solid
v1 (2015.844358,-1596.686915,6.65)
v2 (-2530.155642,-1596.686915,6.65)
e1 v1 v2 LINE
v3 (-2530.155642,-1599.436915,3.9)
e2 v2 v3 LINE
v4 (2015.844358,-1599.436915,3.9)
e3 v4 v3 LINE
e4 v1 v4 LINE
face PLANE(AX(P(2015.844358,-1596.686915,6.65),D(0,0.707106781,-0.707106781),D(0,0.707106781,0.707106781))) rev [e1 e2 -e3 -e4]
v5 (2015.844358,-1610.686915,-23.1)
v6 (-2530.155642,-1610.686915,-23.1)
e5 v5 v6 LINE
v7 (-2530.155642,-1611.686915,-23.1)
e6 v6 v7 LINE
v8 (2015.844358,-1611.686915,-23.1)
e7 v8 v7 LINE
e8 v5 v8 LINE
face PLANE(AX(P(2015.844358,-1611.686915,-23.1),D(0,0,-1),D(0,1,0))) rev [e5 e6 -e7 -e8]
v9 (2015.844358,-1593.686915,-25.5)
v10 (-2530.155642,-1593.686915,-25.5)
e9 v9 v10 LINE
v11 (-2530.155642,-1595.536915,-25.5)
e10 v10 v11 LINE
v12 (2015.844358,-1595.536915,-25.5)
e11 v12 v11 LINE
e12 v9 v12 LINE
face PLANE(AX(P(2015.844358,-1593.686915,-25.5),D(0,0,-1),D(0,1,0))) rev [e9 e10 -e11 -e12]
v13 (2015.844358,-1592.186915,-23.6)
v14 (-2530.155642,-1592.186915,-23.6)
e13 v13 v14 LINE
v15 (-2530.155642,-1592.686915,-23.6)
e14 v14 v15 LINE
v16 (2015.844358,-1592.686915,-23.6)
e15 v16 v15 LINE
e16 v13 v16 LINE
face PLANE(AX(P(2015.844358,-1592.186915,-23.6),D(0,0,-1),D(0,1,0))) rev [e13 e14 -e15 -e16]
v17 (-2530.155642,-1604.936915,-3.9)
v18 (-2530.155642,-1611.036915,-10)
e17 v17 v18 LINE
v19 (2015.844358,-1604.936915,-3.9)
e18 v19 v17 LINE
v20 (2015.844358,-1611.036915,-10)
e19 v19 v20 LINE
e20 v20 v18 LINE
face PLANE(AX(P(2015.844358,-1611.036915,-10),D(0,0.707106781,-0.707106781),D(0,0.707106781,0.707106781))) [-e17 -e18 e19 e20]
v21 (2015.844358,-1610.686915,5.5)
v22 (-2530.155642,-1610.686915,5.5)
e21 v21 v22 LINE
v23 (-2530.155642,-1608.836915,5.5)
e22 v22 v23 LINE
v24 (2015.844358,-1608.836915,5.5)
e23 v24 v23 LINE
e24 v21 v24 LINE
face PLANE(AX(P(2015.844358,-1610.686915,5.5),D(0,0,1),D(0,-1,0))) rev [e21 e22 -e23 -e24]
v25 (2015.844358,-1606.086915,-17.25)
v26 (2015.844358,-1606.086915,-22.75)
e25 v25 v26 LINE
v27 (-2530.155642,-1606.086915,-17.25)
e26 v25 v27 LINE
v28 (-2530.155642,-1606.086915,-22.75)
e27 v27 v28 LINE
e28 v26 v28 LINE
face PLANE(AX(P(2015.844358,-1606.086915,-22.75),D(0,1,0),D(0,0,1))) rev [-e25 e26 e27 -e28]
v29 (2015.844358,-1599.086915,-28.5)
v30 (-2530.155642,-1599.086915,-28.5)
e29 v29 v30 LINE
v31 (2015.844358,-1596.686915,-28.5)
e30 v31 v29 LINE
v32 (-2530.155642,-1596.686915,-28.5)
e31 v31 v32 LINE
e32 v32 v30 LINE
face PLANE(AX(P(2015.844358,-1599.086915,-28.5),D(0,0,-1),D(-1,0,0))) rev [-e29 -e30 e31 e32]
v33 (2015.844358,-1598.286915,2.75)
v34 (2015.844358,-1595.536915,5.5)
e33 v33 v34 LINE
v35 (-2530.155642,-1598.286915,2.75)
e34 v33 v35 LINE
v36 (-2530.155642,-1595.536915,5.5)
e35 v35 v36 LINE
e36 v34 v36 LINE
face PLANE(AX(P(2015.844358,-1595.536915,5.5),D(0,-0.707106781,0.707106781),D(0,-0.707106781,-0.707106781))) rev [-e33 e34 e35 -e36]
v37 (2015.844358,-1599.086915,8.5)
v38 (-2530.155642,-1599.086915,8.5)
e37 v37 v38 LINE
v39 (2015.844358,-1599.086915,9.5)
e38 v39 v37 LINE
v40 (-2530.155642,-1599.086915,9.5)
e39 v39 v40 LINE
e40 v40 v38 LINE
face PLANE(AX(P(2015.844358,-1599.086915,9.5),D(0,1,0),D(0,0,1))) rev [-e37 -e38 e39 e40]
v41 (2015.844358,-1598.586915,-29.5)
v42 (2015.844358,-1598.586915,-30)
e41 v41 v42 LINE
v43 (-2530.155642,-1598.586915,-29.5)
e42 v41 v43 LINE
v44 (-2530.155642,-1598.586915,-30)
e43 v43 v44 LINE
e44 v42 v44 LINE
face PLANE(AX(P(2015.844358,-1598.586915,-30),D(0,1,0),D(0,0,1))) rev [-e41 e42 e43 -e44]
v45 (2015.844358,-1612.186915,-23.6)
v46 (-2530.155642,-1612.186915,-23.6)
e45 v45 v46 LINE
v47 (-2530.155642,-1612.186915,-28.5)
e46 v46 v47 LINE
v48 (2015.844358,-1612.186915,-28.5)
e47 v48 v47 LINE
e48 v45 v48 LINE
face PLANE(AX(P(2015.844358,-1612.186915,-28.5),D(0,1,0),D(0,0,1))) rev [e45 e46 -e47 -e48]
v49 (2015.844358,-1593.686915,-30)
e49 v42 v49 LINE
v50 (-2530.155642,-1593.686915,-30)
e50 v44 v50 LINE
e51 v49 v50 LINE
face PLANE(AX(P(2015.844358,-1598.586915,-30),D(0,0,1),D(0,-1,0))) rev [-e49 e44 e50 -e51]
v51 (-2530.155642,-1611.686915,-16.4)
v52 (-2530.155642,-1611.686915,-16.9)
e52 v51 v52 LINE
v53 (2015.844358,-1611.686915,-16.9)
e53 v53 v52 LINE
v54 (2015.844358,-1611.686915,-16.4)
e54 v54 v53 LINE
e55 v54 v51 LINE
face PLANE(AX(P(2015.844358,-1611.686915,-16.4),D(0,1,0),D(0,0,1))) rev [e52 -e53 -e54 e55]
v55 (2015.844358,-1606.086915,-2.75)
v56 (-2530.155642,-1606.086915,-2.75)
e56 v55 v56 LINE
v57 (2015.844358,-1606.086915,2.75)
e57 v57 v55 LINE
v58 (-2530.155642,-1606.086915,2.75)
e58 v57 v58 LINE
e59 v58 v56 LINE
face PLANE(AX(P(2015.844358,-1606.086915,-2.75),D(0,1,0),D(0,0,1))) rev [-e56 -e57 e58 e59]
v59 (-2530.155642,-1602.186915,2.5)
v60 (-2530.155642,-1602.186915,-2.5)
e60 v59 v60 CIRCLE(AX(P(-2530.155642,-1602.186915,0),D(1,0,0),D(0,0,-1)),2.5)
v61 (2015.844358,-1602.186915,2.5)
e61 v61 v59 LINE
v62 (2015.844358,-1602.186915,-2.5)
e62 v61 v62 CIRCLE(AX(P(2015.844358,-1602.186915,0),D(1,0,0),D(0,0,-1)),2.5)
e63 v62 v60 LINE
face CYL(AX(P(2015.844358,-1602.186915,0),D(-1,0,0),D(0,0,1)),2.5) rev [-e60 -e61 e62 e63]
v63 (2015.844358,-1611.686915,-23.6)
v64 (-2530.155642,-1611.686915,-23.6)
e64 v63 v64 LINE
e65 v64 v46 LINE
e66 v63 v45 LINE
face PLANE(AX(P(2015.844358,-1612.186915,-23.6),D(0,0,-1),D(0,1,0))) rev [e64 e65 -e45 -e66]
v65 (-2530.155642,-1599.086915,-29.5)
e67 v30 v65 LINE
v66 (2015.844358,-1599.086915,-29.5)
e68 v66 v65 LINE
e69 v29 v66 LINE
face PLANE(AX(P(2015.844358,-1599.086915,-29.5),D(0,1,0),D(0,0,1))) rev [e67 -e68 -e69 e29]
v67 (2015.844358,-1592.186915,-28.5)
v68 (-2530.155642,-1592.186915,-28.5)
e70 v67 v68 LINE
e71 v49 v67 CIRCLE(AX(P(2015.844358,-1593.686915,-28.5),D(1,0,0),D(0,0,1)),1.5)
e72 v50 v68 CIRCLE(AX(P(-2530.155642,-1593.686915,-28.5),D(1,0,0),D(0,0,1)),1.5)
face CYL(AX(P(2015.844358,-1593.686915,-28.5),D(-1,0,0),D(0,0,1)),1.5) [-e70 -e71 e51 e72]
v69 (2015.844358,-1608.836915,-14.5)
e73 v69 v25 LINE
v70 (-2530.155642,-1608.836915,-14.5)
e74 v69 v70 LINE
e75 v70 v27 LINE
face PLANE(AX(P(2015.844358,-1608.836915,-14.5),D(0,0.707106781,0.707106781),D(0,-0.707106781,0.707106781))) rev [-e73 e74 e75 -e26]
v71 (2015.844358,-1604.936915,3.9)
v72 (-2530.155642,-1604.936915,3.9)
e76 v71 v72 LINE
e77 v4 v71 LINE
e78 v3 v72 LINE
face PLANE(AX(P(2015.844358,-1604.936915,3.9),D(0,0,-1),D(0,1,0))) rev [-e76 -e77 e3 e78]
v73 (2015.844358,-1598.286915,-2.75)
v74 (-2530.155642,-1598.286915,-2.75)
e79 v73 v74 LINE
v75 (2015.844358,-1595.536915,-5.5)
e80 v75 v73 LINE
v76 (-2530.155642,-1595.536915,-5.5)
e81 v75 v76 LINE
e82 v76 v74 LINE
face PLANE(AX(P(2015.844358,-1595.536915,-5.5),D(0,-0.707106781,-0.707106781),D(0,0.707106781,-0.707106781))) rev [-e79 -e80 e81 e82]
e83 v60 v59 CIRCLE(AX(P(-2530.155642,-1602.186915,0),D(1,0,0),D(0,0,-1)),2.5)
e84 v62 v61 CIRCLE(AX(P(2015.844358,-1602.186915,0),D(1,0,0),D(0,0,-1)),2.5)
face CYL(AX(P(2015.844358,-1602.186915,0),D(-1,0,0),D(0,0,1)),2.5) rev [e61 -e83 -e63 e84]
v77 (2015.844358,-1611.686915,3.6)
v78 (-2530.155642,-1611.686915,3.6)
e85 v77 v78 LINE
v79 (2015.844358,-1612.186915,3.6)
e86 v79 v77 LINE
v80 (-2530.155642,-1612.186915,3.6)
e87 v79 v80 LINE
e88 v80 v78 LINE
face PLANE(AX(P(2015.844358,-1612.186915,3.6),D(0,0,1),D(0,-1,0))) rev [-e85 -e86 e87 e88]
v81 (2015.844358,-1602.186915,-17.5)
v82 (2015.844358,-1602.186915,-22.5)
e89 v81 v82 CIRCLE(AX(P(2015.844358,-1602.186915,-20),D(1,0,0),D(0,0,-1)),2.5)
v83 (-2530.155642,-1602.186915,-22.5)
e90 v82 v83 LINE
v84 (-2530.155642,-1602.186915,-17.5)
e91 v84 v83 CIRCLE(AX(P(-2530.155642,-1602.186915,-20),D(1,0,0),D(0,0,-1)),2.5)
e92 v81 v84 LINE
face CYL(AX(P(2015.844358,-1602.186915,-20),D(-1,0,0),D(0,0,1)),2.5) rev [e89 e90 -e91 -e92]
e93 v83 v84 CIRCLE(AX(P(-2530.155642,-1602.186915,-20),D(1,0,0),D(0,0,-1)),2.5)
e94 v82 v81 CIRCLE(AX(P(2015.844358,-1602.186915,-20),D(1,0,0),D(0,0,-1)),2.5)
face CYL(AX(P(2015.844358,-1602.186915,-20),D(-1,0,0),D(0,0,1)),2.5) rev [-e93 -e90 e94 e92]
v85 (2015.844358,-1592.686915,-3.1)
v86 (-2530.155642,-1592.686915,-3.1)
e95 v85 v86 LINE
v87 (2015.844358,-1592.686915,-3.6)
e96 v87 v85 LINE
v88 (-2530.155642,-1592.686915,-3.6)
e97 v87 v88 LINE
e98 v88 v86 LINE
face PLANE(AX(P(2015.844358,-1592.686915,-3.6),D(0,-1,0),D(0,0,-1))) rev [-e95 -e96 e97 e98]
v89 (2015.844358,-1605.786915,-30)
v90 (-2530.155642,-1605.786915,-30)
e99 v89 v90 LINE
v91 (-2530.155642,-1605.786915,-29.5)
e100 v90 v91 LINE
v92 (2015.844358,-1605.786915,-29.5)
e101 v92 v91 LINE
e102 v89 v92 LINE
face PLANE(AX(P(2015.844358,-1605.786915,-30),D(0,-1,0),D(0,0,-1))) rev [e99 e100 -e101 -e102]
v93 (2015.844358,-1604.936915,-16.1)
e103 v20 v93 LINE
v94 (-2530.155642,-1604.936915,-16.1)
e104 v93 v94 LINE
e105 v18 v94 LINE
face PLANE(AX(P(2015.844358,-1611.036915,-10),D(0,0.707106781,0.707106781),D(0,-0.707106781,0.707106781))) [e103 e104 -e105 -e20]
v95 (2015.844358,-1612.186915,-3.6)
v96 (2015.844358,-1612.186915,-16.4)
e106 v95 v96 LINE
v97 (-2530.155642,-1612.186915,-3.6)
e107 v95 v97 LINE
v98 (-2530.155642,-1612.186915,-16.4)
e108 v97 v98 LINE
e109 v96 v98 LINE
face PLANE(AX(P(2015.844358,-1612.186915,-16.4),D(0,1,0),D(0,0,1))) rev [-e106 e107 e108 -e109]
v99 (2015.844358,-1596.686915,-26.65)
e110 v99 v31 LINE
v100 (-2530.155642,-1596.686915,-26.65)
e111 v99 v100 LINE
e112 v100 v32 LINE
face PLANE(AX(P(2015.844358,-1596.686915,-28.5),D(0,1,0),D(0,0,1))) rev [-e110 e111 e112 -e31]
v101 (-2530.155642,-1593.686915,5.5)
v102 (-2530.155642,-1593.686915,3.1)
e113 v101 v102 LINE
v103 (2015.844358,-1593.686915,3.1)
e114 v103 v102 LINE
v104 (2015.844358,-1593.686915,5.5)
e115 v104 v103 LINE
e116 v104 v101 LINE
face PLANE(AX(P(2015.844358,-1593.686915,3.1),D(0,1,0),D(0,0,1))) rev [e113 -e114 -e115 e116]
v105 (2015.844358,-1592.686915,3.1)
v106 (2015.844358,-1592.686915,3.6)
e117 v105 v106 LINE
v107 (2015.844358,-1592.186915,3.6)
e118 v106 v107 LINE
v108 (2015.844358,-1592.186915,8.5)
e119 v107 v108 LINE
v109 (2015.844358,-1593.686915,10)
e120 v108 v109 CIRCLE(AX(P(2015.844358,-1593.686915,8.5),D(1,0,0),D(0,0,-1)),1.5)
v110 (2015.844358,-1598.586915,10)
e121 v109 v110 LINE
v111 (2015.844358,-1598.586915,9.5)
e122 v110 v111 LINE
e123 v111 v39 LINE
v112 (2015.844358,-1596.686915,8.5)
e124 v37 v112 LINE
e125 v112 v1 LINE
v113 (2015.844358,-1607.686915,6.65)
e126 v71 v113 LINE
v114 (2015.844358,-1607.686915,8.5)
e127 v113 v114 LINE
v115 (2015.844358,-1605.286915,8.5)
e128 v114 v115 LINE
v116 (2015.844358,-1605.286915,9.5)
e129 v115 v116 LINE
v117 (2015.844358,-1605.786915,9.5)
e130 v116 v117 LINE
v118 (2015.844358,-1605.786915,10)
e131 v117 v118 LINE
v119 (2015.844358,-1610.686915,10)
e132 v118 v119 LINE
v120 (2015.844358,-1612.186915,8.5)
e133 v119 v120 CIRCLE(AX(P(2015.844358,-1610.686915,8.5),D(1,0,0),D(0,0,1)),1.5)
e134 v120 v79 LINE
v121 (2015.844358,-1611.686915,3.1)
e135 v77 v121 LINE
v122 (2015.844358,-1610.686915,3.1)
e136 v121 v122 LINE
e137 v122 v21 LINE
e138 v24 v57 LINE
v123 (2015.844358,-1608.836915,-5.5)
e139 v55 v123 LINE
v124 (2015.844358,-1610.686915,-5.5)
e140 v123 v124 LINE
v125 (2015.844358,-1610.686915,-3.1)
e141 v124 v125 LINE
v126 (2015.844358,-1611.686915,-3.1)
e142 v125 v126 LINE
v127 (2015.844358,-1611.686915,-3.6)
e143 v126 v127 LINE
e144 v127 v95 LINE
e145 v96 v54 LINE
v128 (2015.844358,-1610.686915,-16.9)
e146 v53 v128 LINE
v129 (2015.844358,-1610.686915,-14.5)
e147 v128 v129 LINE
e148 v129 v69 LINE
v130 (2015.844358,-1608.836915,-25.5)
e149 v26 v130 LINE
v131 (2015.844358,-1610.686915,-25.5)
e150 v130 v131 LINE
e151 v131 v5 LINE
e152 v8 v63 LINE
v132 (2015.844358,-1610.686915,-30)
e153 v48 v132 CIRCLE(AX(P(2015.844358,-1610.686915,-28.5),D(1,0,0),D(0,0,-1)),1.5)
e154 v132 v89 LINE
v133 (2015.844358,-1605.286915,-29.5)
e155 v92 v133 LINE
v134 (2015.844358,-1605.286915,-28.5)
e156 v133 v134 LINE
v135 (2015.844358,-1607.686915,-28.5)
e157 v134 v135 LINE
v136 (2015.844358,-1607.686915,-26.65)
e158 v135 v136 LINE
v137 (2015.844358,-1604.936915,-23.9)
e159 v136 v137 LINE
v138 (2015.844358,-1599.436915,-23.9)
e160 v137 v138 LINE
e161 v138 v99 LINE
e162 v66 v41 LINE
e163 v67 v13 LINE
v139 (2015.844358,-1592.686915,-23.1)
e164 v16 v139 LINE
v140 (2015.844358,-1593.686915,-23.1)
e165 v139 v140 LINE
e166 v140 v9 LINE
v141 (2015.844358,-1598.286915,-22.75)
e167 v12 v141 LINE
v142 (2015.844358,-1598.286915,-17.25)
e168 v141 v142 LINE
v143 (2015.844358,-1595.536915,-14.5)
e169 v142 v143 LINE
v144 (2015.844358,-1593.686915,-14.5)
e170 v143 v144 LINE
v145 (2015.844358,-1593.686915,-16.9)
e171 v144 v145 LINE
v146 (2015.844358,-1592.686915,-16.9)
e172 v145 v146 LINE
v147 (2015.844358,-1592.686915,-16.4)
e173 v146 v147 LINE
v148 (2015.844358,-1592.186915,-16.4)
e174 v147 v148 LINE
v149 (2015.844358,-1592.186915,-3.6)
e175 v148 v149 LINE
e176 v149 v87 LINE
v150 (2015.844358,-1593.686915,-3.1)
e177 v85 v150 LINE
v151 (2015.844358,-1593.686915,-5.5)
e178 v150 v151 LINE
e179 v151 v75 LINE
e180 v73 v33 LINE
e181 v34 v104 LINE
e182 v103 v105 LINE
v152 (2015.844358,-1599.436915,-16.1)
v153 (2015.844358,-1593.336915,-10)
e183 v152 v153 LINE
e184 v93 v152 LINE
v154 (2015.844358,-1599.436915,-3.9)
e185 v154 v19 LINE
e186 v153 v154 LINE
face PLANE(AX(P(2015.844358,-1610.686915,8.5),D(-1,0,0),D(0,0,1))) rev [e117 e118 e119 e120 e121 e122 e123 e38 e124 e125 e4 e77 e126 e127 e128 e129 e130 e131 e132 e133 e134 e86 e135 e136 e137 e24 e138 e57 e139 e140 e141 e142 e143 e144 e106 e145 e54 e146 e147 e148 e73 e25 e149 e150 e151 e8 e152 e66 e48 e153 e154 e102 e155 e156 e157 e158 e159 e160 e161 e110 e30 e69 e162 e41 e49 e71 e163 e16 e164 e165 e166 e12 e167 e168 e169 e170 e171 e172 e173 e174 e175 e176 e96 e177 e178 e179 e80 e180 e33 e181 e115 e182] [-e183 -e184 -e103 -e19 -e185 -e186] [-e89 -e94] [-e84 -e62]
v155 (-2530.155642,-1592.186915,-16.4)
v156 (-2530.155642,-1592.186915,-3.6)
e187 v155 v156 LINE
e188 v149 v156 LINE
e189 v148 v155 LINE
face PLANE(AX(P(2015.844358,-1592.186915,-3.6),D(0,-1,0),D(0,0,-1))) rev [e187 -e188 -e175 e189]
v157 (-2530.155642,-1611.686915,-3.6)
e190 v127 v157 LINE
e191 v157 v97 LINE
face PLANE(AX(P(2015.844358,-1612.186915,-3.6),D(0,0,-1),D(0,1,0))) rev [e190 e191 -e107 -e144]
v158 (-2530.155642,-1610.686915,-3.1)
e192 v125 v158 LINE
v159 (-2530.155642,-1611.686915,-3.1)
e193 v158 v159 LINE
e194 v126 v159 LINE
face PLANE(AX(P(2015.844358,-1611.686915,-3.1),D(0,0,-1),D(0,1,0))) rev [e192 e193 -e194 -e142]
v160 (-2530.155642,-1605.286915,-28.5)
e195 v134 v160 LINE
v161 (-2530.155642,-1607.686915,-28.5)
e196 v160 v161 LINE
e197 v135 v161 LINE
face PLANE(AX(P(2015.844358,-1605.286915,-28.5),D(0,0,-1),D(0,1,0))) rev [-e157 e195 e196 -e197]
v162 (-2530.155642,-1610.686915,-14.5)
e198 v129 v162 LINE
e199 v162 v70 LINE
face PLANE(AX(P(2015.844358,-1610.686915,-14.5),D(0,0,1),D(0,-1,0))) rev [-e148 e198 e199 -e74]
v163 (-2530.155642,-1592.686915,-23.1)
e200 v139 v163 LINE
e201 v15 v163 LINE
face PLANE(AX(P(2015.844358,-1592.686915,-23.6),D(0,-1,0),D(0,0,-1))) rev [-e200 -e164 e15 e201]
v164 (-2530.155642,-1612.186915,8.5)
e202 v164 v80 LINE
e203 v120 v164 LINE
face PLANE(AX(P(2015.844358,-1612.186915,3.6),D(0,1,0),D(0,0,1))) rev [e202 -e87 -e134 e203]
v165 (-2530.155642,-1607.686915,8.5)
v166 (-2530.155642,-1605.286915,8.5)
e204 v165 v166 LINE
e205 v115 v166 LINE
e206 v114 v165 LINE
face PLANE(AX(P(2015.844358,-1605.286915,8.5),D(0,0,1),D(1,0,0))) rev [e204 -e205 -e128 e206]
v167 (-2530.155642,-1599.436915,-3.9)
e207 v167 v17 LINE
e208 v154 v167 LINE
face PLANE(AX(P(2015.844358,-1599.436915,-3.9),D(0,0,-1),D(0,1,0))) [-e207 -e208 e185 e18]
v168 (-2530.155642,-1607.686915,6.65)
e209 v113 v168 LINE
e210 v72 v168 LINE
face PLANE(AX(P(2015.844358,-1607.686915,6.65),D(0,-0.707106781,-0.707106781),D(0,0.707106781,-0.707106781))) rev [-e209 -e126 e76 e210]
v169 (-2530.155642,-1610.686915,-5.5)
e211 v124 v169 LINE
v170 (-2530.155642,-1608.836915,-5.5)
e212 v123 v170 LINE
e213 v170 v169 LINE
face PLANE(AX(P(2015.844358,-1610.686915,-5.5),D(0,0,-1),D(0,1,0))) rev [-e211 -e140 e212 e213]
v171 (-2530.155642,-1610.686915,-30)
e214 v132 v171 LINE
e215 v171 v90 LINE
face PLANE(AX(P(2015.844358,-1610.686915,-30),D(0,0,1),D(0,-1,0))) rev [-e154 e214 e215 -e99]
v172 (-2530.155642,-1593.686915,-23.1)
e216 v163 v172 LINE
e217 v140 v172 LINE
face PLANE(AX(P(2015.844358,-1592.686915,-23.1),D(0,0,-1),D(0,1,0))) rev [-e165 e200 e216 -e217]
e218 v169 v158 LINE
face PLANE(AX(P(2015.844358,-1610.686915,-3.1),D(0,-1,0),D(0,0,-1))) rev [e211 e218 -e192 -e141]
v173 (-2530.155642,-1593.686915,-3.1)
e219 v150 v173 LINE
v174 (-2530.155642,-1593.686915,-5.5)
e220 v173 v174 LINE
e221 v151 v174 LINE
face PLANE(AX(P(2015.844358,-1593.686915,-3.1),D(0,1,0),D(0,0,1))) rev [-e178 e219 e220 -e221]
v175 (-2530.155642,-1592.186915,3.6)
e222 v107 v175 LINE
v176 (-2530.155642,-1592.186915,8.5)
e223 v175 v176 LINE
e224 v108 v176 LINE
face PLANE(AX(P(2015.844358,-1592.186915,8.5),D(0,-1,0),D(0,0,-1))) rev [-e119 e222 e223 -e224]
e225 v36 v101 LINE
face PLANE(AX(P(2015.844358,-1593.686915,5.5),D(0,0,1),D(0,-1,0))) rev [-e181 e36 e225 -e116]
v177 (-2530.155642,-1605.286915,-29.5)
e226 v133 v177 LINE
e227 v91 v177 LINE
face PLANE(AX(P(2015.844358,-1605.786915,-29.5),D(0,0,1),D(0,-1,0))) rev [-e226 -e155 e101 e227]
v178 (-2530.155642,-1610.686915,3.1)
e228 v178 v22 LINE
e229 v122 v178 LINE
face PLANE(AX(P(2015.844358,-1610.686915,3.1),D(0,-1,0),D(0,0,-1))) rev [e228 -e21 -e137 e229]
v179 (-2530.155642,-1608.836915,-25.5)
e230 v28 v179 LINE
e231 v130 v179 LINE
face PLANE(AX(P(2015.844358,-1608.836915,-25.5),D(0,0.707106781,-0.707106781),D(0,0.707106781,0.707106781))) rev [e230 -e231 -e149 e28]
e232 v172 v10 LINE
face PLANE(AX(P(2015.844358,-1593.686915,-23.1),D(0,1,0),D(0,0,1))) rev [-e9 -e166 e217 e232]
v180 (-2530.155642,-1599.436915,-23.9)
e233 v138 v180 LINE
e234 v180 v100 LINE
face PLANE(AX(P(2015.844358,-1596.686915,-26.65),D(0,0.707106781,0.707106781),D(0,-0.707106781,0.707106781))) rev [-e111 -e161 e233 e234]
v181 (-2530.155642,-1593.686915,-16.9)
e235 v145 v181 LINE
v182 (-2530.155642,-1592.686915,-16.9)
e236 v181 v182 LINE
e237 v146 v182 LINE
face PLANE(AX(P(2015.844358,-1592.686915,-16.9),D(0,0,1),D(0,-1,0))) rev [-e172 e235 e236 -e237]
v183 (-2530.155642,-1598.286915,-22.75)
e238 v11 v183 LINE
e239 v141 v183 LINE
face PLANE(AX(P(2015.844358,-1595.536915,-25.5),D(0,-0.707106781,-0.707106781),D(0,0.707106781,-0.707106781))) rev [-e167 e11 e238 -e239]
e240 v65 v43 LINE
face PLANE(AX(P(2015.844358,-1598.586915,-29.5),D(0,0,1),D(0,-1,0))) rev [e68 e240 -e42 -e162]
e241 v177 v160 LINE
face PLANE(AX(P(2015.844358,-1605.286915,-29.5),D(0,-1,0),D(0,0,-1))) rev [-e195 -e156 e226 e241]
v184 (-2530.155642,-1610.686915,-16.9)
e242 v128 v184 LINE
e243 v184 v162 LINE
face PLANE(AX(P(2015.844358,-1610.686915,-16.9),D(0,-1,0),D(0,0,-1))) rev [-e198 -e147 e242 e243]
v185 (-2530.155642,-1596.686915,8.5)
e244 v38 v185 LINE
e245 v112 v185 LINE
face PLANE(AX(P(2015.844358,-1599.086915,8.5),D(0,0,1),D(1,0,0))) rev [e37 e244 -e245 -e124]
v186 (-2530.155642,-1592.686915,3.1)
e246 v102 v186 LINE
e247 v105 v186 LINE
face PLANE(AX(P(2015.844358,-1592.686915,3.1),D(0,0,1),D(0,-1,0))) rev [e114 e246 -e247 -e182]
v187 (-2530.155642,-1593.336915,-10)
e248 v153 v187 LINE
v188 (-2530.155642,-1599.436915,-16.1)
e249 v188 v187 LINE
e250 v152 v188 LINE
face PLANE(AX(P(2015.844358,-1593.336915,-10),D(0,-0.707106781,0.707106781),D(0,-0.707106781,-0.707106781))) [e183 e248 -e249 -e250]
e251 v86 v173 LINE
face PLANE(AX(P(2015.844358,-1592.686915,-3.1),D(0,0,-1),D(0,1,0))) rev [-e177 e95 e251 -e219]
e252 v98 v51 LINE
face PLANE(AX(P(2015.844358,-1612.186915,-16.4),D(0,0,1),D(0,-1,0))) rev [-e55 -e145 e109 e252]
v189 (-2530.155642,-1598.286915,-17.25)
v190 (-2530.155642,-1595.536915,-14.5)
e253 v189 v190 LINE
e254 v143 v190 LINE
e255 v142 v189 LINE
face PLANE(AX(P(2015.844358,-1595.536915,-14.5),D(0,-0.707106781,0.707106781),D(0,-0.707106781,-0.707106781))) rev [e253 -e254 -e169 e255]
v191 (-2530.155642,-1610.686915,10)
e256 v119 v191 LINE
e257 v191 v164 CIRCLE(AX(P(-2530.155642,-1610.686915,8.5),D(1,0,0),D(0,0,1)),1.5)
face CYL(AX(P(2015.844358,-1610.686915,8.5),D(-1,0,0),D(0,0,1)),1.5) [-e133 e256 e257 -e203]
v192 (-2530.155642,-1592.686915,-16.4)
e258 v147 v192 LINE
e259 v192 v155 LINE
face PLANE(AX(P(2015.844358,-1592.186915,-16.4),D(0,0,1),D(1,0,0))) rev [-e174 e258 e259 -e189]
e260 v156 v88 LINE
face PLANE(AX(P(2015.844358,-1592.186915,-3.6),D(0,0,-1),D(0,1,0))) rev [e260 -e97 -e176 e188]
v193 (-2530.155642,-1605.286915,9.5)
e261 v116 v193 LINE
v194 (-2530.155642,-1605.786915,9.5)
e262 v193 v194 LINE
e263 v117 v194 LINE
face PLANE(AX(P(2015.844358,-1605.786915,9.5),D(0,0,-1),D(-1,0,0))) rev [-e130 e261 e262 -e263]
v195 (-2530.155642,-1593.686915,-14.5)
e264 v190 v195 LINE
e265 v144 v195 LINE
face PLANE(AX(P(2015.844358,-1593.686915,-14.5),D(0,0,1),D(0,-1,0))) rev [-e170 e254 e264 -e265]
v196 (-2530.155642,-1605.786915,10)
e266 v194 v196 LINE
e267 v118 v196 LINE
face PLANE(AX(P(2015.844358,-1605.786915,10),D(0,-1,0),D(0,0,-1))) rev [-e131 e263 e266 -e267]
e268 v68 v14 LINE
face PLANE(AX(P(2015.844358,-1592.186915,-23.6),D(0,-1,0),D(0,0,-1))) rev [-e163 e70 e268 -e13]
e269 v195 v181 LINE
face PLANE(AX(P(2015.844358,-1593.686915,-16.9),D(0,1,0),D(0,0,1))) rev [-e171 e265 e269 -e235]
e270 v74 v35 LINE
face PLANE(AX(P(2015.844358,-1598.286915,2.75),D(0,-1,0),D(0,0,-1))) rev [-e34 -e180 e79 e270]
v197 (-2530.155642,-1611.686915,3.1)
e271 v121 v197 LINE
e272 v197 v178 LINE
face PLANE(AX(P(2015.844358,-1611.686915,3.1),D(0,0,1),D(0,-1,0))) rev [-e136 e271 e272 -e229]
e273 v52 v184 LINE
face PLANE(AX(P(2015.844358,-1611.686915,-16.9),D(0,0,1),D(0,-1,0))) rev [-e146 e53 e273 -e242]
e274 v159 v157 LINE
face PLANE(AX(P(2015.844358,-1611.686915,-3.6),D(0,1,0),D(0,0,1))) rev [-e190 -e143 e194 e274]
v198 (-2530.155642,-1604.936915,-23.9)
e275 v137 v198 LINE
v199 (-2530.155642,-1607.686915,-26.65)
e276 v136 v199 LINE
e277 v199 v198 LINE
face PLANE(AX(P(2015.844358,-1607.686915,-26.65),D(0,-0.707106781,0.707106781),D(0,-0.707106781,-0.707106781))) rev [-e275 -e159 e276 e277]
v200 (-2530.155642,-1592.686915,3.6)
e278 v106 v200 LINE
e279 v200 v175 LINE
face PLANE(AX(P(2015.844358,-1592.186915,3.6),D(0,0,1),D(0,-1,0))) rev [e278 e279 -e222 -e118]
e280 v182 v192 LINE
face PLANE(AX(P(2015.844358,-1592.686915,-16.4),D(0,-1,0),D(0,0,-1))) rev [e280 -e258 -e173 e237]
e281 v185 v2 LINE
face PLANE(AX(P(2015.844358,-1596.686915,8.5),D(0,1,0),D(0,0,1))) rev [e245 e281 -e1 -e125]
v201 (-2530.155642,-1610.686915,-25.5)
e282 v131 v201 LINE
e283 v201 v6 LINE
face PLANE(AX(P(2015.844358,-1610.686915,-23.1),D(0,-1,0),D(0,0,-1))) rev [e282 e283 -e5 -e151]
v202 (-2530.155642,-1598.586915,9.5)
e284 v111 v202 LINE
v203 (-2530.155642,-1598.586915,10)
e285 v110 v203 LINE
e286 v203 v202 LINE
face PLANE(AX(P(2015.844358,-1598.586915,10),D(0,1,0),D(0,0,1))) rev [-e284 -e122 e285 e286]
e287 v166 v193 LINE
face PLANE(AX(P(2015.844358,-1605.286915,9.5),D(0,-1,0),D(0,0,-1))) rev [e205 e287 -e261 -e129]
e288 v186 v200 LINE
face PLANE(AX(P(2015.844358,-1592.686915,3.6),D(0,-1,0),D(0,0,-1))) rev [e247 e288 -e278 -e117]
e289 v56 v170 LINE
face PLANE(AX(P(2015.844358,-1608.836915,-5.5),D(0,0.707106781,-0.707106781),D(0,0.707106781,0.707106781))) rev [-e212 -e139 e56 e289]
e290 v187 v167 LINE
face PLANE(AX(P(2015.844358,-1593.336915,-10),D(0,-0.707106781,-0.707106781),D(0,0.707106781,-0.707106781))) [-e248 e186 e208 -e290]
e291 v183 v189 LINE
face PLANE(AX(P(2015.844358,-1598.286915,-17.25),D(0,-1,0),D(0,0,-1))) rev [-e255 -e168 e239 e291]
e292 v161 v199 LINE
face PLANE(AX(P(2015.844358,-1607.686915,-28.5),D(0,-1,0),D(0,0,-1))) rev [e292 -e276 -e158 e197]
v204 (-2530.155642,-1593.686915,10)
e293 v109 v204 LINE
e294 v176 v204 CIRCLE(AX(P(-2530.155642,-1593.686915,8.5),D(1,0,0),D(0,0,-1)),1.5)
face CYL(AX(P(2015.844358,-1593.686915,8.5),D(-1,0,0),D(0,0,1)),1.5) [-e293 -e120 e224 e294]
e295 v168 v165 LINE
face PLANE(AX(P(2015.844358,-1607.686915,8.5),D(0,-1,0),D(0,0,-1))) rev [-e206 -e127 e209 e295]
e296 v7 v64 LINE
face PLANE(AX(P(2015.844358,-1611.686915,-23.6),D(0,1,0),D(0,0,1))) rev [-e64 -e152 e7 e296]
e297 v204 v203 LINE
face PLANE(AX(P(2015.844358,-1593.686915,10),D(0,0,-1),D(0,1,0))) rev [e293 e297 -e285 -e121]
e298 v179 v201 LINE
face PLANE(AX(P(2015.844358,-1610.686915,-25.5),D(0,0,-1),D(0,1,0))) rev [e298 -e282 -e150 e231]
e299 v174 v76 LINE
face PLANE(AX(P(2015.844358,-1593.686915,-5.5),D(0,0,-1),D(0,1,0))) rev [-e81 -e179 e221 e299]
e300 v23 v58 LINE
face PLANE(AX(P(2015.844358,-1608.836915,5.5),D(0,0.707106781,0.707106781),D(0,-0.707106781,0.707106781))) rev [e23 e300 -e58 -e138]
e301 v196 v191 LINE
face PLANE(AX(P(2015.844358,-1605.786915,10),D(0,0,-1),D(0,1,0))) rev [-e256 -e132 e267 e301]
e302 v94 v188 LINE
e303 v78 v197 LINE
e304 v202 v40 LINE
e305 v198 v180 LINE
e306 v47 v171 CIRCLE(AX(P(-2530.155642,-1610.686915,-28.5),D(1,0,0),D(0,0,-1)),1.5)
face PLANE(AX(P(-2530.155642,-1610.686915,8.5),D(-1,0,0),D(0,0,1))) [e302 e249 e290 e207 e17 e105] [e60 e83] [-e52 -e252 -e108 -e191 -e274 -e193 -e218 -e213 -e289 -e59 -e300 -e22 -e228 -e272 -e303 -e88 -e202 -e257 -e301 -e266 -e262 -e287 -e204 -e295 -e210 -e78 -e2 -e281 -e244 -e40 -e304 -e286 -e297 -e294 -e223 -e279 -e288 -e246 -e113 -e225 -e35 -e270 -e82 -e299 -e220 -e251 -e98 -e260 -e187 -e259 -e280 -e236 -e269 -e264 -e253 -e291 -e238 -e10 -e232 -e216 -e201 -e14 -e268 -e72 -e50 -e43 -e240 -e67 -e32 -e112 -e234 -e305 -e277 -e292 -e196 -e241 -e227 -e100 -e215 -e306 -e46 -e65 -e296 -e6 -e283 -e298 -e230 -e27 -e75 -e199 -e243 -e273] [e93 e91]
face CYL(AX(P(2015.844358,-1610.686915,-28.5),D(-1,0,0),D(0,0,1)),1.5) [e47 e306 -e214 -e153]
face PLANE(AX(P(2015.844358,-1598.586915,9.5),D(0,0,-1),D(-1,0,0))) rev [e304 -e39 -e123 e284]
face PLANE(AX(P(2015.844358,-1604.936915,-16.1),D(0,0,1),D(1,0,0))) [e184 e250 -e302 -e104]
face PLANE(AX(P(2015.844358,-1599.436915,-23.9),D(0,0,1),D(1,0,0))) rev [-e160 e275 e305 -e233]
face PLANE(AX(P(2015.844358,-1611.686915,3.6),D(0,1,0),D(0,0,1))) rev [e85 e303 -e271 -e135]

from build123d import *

# Parameters (mm, degrees)
SKETCH1_R                               = 2.5
ALUMINUM_PROFILE_20_X_40_X_R1_5_1_DEPTH = 4546
M6_TAPPED_HOLE1_D                       = 5
M6_TAPPED_HOLE1_DEPTH                   = 15
M6_TAPPED_HOLE1_TIP                     = 1.502151548


with BuildPart() as part:
    # Sketch1 → Aluminum profile 20 X 40 X R1.5(1) (new body)
    with BuildSketch(Plane(origin=(-2530.155642023, -1602.186915496, 0), x_dir=(0, 1, 0), z_dir=(1, 0, 0))):
        with BuildLine():
            Line((-3.6, 10), (-3.6, 9.5))
            Line((-3.6, 9.5), (-3.1, 9.5))
            Line((-3.1, 9.5), (-3.1, 8.5))
            Line((-3.1, 8.5), (-5.5, 8.5))
            Line((-5.5, 8.5), (-5.5, 6.65))
            Line((-5.5, 6.65), (-2.75, 3.9))
            Line((-2.75, 3.9), (2.75, 3.9))
            Line((2.75, 3.9), (5.5, 6.65))
            Line((5.5, 6.65), (5.5, 8.5))
            Line((5.5, 8.5), (3.1, 8.5))
            Line((3.1, 8.5), (3.1, 9.5))
            Line((3.1, 9.5), (3.6, 9.5))
            Line((3.6, 9.5), (3.6, 10))
            Line((3.6, 10), (8.5, 10))
            ThreePointArc((8.5, 10), (9.560660172, 9.560660172), (10, 8.5))
            Line((10, 8.5), (10, 3.6))
            Line((10, 3.6), (9.5, 3.6))
            Line((9.5, 3.6), (9.5, 3.1))
            Line((9.5, 3.1), (8.5, 3.1))
            Line((8.5, 3.1), (8.5, 5.5))
            Line((8.5, 5.5), (6.65, 5.5))
            Line((6.65, 5.5), (3.9, 2.75))
            Line((3.9, 2.75), (3.9, -2.75))
            Line((3.9, -2.75), (6.65, -5.5))
            Line((6.65, -5.5), (8.5, -5.5))
            Line((8.5, -5.5), (8.5, -3.1))
            Line((8.5, -3.1), (9.5, -3.1))
            Line((9.5, -3.1), (9.5, -3.6))
            Line((9.5, -3.6), (10, -3.6))
            Line((10, -3.6), (10, -16.4))
            Line((10, -16.4), (9.5, -16.4))
            Line((9.5, -16.4), (9.5, -16.9))
            Line((9.5, -16.9), (8.5, -16.9))
            Line((8.5, -16.9), (8.5, -14.5))
            Line((8.5, -14.5), (6.65, -14.5))
            Line((6.65, -14.5), (3.9, -17.25))
            Line((3.9, -17.25), (3.9, -22.75))
            Line((3.9, -22.75), (6.65, -25.5))
            Line((6.65, -25.5), (8.5, -25.5))
            Line((8.5, -25.5), (8.5, -23.1))
            Line((8.5, -23.1), (9.5, -23.1))
            Line((9.5, -23.1), (9.5, -23.6))
            Line((9.5, -23.6), (10, -23.6))
            Line((10, -23.6), (10, -28.5))
            ThreePointArc((10, -28.5), (9.560660172, -29.560660172), (8.5, -30))
            Line((8.5, -30), (3.6, -30))
            Line((3.6, -30), (3.6, -29.5))
            Line((3.6, -29.5), (3.1, -29.5))
            Line((3.1, -29.5), (3.1, -28.5))
            Line((3.1, -28.5), (5.5, -28.5))
            Line((5.5, -28.5), (5.5, -26.65))
            Line((5.5, -26.65), (2.75, -23.9))
            Line((2.75, -23.9), (-2.75, -23.9))
            Line((-2.75, -23.9), (-5.5, -26.65))
            Line((-5.5, -26.65), (-5.5, -28.5))
            Line((-5.5, -28.5), (-3.1, -28.5))
            Line((-3.1, -28.5), (-3.1, -29.5))
            Line((-3.1, -29.5), (-3.6, -29.5))
            Line((-3.6, -29.5), (-3.6, -30))
            Line((-3.6, -30), (-8.5, -30))
            ThreePointArc((-8.5, -30), (-9.560660172, -29.560660172), (-10, -28.5))
            Line((-10, -28.5), (-10, -23.6))
            Line((-10, -23.6), (-9.5, -23.6))
            Line((-9.5, -23.6), (-9.5, -23.1))
            Line((-9.5, -23.1), (-8.5, -23.1))
            Line((-8.5, -23.1), (-8.5, -25.5))
            Line((-8.5, -25.5), (-6.65, -25.5))
            Line((-6.65, -25.5), (-3.9, -22.75))
            Line((-3.9, -22.75), (-3.9, -17.25))
            Line((-3.9, -17.25), (-6.65, -14.5))
            Line((-6.65, -14.5), (-8.5, -14.5))
            Line((-8.5, -14.5), (-8.5, -16.9))
            Line((-8.5, -16.9), (-9.5, -16.9))
            Line((-9.5, -16.9), (-9.5, -16.4))
            Line((-9.5, -16.4), (-10, -16.4))
            Line((-10, -16.4), (-10, -3.6))
            Line((-10, -3.6), (-9.5, -3.6))
            Line((-9.5, -3.6), (-9.5, -3.1))
            Line((-9.5, -3.1), (-8.5, -3.1))
            Line((-8.5, -3.1), (-8.5, -5.5))
            Line((-8.5, -5.5), (-6.65, -5.5))
            Line((-6.65, -5.5), (-3.9, -2.75))
            Line((-3.9, -2.75), (-3.9, 2.75))
            Line((-3.9, 2.75), (-6.65, 5.5))
            Line((-6.65, 5.5), (-8.5, 5.5))
            Line((-8.5, 5.5), (-8.5, 3.1))
            Line((-8.5, 3.1), (-9.5, 3.1))
            Line((-9.5, 3.1), (-9.5, 3.6))
            Line((-9.5, 3.6), (-10, 3.6))
            Line((-10, 3.6), (-10, 8.5))
            ThreePointArc((-10, 8.5), (-9.560660172, 9.560660172), (-8.5, 10))
            Line((-8.5, 10), (-3.6, 10))
        make_face()
        Circle(SKETCH1_R, mode=Mode.SUBTRACT)
        with Locations((0, -20)):
            Circle(SKETCH1_R, mode=Mode.SUBTRACT)
        Polygon((8.85, -10), (2.75, -3.9), (-2.75, -3.9), (-8.85, -10), (-2.75, -16.1), (2.75, -16.1), align=None, mode=Mode.SUBTRACT)
    extrude(amount=ALUMINUM_PROFILE_20_X_40_X_R1_5_1_DEPTH)

    # M6 Tapped Hole1
    with Locations(Plane(origin=(2015.844357977, 0, 0), x_dir=(0, 0, -1), z_dir=(1, 0, 0))):
        with Locations((0, -1602.186915496), (20, -1602.186915496)):
            Hole(M6_TAPPED_HOLE1_D / 2, depth=M6_TAPPED_HOLE1_DEPTH)
            with Locations((0, 0, -(M6_TAPPED_HOLE1_DEPTH + M6_TAPPED_HOLE1_TIP / 2))):  # 118° drill point
                Cone(0, M6_TAPPED_HOLE1_D / 2, M6_TAPPED_HOLE1_TIP, mode=Mode.SUBTRACT)


solid = part.part
